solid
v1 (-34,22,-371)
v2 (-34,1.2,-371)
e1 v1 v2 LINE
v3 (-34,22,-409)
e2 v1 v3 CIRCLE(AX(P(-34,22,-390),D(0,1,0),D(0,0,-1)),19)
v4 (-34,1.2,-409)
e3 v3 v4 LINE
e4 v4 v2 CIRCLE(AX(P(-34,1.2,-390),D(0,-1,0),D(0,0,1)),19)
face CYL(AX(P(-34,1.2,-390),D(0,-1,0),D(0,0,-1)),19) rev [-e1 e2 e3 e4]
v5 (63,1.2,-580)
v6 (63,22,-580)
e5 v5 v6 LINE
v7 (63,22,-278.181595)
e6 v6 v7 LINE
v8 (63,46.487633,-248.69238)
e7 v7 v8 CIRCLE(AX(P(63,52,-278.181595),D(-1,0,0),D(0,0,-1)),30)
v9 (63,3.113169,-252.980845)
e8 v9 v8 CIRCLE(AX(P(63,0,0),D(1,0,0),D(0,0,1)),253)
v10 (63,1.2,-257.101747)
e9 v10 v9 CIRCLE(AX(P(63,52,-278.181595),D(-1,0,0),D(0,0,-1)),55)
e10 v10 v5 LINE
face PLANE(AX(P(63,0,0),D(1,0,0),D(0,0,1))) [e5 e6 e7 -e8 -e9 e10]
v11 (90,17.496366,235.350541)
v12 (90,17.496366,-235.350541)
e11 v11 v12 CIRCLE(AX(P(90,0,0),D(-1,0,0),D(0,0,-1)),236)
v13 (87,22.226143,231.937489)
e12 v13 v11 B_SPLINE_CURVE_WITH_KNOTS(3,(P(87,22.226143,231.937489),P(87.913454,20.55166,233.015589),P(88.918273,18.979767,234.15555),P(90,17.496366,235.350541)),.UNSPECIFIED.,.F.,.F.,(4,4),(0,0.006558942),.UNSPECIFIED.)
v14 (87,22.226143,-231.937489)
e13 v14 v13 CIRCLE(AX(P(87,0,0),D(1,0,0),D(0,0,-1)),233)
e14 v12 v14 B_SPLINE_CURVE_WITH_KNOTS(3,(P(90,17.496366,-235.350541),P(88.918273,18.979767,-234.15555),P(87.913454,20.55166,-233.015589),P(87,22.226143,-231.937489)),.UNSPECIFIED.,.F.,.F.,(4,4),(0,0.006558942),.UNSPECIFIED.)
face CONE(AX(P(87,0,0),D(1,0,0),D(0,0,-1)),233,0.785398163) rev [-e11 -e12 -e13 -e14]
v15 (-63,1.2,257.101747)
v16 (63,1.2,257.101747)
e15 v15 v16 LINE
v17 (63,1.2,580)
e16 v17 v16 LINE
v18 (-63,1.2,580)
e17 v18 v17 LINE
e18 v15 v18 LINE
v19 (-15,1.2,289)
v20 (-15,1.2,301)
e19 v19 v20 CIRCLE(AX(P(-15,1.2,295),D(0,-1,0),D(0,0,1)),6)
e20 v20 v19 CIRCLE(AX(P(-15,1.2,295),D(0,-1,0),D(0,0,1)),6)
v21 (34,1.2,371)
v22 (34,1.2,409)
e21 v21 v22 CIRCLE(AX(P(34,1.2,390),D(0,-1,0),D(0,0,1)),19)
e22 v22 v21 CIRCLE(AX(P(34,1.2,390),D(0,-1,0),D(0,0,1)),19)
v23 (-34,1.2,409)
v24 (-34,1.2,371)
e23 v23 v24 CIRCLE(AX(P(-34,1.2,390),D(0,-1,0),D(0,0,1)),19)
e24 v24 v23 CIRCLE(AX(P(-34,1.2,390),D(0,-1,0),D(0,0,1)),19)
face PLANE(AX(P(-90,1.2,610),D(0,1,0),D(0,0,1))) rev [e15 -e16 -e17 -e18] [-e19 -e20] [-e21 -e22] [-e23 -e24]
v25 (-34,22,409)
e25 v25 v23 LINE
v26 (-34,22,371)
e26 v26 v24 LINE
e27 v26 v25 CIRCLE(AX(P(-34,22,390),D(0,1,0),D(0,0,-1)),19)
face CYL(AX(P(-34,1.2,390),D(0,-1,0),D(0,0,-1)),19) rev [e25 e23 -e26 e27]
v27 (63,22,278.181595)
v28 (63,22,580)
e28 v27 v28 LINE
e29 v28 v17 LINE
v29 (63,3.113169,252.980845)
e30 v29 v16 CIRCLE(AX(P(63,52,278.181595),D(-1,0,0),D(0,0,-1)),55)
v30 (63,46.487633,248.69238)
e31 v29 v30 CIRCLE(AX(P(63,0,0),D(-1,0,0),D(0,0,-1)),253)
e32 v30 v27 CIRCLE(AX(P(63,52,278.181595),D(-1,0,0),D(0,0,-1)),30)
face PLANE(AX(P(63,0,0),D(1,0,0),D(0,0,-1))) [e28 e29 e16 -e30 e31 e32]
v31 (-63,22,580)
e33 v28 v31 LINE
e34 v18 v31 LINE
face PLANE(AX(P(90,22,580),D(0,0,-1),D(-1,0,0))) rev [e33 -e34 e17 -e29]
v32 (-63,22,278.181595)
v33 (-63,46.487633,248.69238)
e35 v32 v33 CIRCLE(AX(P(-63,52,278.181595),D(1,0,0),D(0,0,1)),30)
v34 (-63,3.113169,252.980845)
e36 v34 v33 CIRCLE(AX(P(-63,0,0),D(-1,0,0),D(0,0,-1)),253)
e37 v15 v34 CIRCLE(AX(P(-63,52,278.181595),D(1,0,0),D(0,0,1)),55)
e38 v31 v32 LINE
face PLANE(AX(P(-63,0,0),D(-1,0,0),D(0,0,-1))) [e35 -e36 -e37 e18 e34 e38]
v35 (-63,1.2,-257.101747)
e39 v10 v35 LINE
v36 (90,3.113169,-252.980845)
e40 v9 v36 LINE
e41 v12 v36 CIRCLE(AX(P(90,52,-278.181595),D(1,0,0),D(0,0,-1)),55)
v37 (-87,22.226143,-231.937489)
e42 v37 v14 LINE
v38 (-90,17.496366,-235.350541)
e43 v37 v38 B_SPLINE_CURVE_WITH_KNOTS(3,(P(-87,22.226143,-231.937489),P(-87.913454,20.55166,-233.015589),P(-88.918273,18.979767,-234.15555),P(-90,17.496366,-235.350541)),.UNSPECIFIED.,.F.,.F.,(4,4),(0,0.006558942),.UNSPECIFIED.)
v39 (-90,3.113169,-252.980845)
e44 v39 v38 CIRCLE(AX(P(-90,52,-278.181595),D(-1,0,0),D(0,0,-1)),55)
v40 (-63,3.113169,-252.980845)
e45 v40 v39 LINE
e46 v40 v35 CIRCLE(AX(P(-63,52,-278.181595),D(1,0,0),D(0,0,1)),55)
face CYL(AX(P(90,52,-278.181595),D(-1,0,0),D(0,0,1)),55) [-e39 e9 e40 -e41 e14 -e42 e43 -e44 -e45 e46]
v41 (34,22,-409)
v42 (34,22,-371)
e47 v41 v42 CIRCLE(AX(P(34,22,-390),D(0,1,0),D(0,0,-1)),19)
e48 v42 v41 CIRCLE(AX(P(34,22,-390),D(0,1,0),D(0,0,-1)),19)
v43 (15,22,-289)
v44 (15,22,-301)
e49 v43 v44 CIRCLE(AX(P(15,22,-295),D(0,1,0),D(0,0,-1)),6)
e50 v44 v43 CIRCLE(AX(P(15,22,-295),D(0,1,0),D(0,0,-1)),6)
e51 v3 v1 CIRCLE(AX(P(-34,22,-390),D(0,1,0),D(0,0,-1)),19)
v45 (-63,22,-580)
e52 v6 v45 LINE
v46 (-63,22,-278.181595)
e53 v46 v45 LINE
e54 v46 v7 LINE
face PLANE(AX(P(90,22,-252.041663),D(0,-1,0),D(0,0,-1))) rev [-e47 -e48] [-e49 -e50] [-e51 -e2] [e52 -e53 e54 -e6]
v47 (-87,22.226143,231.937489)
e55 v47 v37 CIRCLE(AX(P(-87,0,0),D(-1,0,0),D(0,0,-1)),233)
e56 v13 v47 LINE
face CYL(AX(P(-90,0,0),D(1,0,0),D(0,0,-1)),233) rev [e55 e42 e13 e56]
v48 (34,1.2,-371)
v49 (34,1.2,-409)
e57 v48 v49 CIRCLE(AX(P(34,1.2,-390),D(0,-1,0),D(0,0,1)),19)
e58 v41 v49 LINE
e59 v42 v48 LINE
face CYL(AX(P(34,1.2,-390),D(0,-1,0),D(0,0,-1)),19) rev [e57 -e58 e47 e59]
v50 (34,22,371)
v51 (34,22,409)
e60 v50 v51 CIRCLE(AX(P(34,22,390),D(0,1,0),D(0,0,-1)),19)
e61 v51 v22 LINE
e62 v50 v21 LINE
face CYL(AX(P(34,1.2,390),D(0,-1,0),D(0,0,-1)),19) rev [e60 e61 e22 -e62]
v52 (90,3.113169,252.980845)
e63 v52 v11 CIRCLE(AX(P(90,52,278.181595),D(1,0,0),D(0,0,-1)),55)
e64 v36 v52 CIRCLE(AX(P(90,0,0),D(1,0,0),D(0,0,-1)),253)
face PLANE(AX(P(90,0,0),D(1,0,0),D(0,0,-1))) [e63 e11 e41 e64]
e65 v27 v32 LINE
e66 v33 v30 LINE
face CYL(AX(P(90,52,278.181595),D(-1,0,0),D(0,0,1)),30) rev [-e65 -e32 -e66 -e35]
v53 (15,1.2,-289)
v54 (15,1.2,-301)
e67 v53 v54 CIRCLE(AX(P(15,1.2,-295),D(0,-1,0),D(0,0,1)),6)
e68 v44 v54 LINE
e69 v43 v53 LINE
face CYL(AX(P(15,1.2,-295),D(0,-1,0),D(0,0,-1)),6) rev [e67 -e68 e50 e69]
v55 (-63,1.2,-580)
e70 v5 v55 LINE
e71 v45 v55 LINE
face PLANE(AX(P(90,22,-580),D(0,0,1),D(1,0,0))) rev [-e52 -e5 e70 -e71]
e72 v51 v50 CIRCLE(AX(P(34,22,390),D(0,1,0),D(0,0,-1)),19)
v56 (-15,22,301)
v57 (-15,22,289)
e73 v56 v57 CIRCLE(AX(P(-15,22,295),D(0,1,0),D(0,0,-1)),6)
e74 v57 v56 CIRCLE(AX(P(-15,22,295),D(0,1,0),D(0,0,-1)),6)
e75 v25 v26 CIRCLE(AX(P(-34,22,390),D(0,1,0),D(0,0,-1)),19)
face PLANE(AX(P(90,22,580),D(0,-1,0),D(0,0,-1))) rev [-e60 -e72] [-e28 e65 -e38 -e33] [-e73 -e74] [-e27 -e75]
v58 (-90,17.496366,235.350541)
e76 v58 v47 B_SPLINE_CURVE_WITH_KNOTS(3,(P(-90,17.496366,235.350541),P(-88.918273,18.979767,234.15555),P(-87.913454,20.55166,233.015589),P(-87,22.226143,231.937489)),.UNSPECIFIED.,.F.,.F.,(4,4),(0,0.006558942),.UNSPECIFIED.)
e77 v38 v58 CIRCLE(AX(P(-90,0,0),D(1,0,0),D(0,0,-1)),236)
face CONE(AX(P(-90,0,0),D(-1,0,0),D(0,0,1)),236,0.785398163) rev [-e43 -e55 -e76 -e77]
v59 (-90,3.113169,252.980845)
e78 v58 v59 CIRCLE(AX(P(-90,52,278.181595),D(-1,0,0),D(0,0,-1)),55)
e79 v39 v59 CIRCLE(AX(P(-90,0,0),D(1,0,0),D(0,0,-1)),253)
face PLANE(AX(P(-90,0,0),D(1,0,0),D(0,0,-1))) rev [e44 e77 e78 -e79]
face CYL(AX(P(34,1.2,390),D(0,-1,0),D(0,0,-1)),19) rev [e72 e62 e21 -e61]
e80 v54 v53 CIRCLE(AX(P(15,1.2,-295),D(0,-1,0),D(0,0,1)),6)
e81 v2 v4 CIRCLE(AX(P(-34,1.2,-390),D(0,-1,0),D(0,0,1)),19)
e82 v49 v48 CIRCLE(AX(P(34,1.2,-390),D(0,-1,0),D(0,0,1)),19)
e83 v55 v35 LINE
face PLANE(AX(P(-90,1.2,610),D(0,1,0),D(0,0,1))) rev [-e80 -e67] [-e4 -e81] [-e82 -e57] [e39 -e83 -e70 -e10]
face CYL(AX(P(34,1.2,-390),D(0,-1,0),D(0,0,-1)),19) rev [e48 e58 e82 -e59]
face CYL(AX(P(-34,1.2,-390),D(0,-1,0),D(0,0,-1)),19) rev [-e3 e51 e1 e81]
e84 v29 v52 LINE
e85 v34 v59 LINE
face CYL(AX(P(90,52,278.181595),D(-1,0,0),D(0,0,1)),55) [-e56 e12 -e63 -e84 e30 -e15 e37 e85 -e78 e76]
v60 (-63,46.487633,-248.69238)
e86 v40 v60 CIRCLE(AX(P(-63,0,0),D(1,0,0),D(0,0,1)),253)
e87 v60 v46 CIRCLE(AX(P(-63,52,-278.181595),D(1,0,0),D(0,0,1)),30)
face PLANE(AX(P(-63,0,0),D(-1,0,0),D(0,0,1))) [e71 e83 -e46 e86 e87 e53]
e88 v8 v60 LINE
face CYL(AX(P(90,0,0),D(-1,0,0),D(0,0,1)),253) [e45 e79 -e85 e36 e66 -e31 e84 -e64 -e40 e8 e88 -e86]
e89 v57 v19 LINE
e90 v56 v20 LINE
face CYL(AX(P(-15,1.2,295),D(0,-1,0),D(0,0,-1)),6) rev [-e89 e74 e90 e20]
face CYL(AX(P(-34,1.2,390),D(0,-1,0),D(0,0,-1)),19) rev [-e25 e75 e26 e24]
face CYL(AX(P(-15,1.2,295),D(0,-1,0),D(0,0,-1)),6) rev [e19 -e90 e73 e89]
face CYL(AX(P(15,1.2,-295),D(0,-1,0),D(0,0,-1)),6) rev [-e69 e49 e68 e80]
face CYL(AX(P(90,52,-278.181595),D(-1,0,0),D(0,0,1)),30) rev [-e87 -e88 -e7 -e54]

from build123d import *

# Parameters (mm, degrees)
BOSS_EXTRUDE1_DEPTH     = 90
FILLET1_R               = 30
FILLET2_R               = 55
CUT_EXTRUDE1_DEPTH      = 640.147087923
CUT_EXTRUDE1_DEPTH_BACK = 640.147087923
SKETCH2_R               = 233
CUT_EXTRUDE2_DEPTH      = 640.147087923
CUT_EXTRUDE2_DEPTH_BACK = 640.147087923
SKETCH3_W               = 1220
SKETCH3_H               = 21.2
CUT_EXTRUDE3_DEPTH      = 27
MIRROR2_COPY_1_DEPTH    = 27
CUT_EXTRUDE4_DEPTH      = 640.147087923
CUT_EXTRUDE4_DEPTH_BACK = 640.147087923
SKETCH5_R               = 19
SKETCH5_R_2             = 6
CHAMFER1_SIZE           = 3


with BuildPart() as part:
    # Sketch1 → Boss-Extrude1 (new, symmetric)
    with BuildSketch(Plane(origin=(0, 0, 0), x_dir=(0, 0, -1), z_dir=(1, 0, 0))):
        with BuildLine():
            Line((-580, 22), (-252.041663223, 22))
            ThreePointArc((-252.041663223, 22), (0, 253), (252.041663223, 22))
            Line((252.041663223, 22), (580, 22))
            Line((580, 22), (580, -3))
            Line((580, -3), (227.980262304, -3))
            ThreePointArc((227.980262304, -3), (0, 228), (-227.980262304, -3))
            Line((-227.980262304, -3), (-580, -3))
            Line((-580, -3), (-580, 22))
        make_face()
    extrude(amount=BOSS_EXTRUDE1_DEPTH, both=True)

    # Fillet1
    fillet1_edges = [part.edges().sort_by_distance(p)[0] for p in [
        (0, 22, 252.041663223),
        (0, 22, -252.041663223),
    ]]
    fillet(fillet1_edges, radius=FILLET1_R)

    # Fillet2
    fillet2_edges = [part.edges().sort_by_distance(p)[0] for p in [
        (0, -3, -227.980262304),
        (0, -3, 227.980262304),
    ]]
    fillet(fillet2_edges, radius=FILLET2_R)

    # Sketch2 → Cut-Extrude1 (cut, two sides: drawn at the far end of the back side and taken through both)
    with BuildSketch(Plane(origin=(0, 0, 0), x_dir=(0, 0, -1), z_dir=(1, 0, 0)).offset(-CUT_EXTRUDE1_DEPTH_BACK)):
        Circle(SKETCH2_R)
    extrude(amount=CUT_EXTRUDE1_DEPTH + CUT_EXTRUDE1_DEPTH_BACK, mode=Mode.SUBTRACT)

    # Sketch3 → Cut-Extrude2 (cut, two sides: drawn at the far end of the back side and taken through both)
    with BuildSketch(Plane(origin=(0, 0, 0), x_dir=(0, 0, -1), z_dir=(1, 0, 0)).offset(-CUT_EXTRUDE2_DEPTH_BACK)):
        with Locations((0, -9.4)):
            Rectangle(SKETCH3_W, SKETCH3_H)
    extrude(amount=CUT_EXTRUDE2_DEPTH + CUT_EXTRUDE2_DEPTH_BACK, mode=Mode.SUBTRACT)

    # Sketch4 → Cut-Extrude3 (cut)
    with BuildSketch(Plane(origin=(90, 0, 0), x_dir=(0, 0, -1), z_dir=(1, 0, 0))):
        with BuildLine():
            Line((-598.01008044, 50), (-248.01008044, 50))
            ThreePointArc((-248.01008044, 50), (-252.546221213, 15.14615962), (-252.208247288, -20))
            Line((-252.208247288, -20), (-598.01008044, -20))
            Line((-598.01008044, -20), (-598.01008044, 50))
        make_face()
    cut_extrude3 = extrude(amount=-CUT_EXTRUDE3_DEPTH, mode=Mode.SUBTRACT)

    # Mirror1: Cut-Extrude3 across plane
    add(cut_extrude3.mirror(Plane.XY), mode=Mode.SUBTRACT)

    # Mirror2: Cut-Extrude3 across plane
    add(cut_extrude3.mirror(Plane(origin=(0, 0, 0), x_dir=(0, 0, 1), z_dir=(1, 0, 0))), mode=Mode.SUBTRACT)

    # Mirror2 copy 1 sketch → Mirror2 copy 1 (cut)
    with BuildSketch(Plane.ZY.offset(90)):
        with BuildLine():
            Line((-598.01008044, 50), (-248.01008044, 50))
            ThreePointArc((-248.01008044, 50), (-252.546221213, 15.14615962), (-252.208247288, -20))
            Line((-252.208247288, -20), (-598.01008044, -20))
            Line((-598.01008044, -20), (-598.01008044, 50))
        make_face()
    extrude(amount=-MIRROR2_COPY_1_DEPTH, mode=Mode.SUBTRACT)

    # Sketch5 → Cut-Extrude4 (cut, two sides: drawn at the far end of the back side and taken through both)
    with BuildSketch(Plane(origin=(0, 0, 0), x_dir=(1, 0, 0), z_dir=(0, 1, 0)).offset(-CUT_EXTRUDE4_DEPTH_BACK)):
        with Locations(Location((34, -390, 0), (0, 0, 90))):
            Circle(SKETCH5_R)
        with Locations(Location((34, 390, 0), (0, 0, 90))):
            Circle(SKETCH5_R)
        with Locations(Location((-34, -390, 0), (0, 0, 90))):
            Circle(SKETCH5_R)
        with Locations(Location((-34, 390, 0), (0, 0, 90))):
            Circle(SKETCH5_R)
        with Locations(Location((-15, -295, 0), (0, 0, 90))):
            Circle(SKETCH5_R_2)
        with Locations(Location((15, 295, 0), (0, 0, 90))):
            Circle(SKETCH5_R_2)
    extrude(amount=CUT_EXTRUDE4_DEPTH + CUT_EXTRUDE4_DEPTH_BACK, mode=Mode.SUBTRACT)

    # Chamfer1
    chamfer1_edges = [part.edges().sort_by_distance(p)[0] for p in [
        (-90, 233, 0),
        (90, 233, 0),
    ]]
    chamfer(chamfer1_edges, length=CHAMFER1_SIZE)


solid = part.part
